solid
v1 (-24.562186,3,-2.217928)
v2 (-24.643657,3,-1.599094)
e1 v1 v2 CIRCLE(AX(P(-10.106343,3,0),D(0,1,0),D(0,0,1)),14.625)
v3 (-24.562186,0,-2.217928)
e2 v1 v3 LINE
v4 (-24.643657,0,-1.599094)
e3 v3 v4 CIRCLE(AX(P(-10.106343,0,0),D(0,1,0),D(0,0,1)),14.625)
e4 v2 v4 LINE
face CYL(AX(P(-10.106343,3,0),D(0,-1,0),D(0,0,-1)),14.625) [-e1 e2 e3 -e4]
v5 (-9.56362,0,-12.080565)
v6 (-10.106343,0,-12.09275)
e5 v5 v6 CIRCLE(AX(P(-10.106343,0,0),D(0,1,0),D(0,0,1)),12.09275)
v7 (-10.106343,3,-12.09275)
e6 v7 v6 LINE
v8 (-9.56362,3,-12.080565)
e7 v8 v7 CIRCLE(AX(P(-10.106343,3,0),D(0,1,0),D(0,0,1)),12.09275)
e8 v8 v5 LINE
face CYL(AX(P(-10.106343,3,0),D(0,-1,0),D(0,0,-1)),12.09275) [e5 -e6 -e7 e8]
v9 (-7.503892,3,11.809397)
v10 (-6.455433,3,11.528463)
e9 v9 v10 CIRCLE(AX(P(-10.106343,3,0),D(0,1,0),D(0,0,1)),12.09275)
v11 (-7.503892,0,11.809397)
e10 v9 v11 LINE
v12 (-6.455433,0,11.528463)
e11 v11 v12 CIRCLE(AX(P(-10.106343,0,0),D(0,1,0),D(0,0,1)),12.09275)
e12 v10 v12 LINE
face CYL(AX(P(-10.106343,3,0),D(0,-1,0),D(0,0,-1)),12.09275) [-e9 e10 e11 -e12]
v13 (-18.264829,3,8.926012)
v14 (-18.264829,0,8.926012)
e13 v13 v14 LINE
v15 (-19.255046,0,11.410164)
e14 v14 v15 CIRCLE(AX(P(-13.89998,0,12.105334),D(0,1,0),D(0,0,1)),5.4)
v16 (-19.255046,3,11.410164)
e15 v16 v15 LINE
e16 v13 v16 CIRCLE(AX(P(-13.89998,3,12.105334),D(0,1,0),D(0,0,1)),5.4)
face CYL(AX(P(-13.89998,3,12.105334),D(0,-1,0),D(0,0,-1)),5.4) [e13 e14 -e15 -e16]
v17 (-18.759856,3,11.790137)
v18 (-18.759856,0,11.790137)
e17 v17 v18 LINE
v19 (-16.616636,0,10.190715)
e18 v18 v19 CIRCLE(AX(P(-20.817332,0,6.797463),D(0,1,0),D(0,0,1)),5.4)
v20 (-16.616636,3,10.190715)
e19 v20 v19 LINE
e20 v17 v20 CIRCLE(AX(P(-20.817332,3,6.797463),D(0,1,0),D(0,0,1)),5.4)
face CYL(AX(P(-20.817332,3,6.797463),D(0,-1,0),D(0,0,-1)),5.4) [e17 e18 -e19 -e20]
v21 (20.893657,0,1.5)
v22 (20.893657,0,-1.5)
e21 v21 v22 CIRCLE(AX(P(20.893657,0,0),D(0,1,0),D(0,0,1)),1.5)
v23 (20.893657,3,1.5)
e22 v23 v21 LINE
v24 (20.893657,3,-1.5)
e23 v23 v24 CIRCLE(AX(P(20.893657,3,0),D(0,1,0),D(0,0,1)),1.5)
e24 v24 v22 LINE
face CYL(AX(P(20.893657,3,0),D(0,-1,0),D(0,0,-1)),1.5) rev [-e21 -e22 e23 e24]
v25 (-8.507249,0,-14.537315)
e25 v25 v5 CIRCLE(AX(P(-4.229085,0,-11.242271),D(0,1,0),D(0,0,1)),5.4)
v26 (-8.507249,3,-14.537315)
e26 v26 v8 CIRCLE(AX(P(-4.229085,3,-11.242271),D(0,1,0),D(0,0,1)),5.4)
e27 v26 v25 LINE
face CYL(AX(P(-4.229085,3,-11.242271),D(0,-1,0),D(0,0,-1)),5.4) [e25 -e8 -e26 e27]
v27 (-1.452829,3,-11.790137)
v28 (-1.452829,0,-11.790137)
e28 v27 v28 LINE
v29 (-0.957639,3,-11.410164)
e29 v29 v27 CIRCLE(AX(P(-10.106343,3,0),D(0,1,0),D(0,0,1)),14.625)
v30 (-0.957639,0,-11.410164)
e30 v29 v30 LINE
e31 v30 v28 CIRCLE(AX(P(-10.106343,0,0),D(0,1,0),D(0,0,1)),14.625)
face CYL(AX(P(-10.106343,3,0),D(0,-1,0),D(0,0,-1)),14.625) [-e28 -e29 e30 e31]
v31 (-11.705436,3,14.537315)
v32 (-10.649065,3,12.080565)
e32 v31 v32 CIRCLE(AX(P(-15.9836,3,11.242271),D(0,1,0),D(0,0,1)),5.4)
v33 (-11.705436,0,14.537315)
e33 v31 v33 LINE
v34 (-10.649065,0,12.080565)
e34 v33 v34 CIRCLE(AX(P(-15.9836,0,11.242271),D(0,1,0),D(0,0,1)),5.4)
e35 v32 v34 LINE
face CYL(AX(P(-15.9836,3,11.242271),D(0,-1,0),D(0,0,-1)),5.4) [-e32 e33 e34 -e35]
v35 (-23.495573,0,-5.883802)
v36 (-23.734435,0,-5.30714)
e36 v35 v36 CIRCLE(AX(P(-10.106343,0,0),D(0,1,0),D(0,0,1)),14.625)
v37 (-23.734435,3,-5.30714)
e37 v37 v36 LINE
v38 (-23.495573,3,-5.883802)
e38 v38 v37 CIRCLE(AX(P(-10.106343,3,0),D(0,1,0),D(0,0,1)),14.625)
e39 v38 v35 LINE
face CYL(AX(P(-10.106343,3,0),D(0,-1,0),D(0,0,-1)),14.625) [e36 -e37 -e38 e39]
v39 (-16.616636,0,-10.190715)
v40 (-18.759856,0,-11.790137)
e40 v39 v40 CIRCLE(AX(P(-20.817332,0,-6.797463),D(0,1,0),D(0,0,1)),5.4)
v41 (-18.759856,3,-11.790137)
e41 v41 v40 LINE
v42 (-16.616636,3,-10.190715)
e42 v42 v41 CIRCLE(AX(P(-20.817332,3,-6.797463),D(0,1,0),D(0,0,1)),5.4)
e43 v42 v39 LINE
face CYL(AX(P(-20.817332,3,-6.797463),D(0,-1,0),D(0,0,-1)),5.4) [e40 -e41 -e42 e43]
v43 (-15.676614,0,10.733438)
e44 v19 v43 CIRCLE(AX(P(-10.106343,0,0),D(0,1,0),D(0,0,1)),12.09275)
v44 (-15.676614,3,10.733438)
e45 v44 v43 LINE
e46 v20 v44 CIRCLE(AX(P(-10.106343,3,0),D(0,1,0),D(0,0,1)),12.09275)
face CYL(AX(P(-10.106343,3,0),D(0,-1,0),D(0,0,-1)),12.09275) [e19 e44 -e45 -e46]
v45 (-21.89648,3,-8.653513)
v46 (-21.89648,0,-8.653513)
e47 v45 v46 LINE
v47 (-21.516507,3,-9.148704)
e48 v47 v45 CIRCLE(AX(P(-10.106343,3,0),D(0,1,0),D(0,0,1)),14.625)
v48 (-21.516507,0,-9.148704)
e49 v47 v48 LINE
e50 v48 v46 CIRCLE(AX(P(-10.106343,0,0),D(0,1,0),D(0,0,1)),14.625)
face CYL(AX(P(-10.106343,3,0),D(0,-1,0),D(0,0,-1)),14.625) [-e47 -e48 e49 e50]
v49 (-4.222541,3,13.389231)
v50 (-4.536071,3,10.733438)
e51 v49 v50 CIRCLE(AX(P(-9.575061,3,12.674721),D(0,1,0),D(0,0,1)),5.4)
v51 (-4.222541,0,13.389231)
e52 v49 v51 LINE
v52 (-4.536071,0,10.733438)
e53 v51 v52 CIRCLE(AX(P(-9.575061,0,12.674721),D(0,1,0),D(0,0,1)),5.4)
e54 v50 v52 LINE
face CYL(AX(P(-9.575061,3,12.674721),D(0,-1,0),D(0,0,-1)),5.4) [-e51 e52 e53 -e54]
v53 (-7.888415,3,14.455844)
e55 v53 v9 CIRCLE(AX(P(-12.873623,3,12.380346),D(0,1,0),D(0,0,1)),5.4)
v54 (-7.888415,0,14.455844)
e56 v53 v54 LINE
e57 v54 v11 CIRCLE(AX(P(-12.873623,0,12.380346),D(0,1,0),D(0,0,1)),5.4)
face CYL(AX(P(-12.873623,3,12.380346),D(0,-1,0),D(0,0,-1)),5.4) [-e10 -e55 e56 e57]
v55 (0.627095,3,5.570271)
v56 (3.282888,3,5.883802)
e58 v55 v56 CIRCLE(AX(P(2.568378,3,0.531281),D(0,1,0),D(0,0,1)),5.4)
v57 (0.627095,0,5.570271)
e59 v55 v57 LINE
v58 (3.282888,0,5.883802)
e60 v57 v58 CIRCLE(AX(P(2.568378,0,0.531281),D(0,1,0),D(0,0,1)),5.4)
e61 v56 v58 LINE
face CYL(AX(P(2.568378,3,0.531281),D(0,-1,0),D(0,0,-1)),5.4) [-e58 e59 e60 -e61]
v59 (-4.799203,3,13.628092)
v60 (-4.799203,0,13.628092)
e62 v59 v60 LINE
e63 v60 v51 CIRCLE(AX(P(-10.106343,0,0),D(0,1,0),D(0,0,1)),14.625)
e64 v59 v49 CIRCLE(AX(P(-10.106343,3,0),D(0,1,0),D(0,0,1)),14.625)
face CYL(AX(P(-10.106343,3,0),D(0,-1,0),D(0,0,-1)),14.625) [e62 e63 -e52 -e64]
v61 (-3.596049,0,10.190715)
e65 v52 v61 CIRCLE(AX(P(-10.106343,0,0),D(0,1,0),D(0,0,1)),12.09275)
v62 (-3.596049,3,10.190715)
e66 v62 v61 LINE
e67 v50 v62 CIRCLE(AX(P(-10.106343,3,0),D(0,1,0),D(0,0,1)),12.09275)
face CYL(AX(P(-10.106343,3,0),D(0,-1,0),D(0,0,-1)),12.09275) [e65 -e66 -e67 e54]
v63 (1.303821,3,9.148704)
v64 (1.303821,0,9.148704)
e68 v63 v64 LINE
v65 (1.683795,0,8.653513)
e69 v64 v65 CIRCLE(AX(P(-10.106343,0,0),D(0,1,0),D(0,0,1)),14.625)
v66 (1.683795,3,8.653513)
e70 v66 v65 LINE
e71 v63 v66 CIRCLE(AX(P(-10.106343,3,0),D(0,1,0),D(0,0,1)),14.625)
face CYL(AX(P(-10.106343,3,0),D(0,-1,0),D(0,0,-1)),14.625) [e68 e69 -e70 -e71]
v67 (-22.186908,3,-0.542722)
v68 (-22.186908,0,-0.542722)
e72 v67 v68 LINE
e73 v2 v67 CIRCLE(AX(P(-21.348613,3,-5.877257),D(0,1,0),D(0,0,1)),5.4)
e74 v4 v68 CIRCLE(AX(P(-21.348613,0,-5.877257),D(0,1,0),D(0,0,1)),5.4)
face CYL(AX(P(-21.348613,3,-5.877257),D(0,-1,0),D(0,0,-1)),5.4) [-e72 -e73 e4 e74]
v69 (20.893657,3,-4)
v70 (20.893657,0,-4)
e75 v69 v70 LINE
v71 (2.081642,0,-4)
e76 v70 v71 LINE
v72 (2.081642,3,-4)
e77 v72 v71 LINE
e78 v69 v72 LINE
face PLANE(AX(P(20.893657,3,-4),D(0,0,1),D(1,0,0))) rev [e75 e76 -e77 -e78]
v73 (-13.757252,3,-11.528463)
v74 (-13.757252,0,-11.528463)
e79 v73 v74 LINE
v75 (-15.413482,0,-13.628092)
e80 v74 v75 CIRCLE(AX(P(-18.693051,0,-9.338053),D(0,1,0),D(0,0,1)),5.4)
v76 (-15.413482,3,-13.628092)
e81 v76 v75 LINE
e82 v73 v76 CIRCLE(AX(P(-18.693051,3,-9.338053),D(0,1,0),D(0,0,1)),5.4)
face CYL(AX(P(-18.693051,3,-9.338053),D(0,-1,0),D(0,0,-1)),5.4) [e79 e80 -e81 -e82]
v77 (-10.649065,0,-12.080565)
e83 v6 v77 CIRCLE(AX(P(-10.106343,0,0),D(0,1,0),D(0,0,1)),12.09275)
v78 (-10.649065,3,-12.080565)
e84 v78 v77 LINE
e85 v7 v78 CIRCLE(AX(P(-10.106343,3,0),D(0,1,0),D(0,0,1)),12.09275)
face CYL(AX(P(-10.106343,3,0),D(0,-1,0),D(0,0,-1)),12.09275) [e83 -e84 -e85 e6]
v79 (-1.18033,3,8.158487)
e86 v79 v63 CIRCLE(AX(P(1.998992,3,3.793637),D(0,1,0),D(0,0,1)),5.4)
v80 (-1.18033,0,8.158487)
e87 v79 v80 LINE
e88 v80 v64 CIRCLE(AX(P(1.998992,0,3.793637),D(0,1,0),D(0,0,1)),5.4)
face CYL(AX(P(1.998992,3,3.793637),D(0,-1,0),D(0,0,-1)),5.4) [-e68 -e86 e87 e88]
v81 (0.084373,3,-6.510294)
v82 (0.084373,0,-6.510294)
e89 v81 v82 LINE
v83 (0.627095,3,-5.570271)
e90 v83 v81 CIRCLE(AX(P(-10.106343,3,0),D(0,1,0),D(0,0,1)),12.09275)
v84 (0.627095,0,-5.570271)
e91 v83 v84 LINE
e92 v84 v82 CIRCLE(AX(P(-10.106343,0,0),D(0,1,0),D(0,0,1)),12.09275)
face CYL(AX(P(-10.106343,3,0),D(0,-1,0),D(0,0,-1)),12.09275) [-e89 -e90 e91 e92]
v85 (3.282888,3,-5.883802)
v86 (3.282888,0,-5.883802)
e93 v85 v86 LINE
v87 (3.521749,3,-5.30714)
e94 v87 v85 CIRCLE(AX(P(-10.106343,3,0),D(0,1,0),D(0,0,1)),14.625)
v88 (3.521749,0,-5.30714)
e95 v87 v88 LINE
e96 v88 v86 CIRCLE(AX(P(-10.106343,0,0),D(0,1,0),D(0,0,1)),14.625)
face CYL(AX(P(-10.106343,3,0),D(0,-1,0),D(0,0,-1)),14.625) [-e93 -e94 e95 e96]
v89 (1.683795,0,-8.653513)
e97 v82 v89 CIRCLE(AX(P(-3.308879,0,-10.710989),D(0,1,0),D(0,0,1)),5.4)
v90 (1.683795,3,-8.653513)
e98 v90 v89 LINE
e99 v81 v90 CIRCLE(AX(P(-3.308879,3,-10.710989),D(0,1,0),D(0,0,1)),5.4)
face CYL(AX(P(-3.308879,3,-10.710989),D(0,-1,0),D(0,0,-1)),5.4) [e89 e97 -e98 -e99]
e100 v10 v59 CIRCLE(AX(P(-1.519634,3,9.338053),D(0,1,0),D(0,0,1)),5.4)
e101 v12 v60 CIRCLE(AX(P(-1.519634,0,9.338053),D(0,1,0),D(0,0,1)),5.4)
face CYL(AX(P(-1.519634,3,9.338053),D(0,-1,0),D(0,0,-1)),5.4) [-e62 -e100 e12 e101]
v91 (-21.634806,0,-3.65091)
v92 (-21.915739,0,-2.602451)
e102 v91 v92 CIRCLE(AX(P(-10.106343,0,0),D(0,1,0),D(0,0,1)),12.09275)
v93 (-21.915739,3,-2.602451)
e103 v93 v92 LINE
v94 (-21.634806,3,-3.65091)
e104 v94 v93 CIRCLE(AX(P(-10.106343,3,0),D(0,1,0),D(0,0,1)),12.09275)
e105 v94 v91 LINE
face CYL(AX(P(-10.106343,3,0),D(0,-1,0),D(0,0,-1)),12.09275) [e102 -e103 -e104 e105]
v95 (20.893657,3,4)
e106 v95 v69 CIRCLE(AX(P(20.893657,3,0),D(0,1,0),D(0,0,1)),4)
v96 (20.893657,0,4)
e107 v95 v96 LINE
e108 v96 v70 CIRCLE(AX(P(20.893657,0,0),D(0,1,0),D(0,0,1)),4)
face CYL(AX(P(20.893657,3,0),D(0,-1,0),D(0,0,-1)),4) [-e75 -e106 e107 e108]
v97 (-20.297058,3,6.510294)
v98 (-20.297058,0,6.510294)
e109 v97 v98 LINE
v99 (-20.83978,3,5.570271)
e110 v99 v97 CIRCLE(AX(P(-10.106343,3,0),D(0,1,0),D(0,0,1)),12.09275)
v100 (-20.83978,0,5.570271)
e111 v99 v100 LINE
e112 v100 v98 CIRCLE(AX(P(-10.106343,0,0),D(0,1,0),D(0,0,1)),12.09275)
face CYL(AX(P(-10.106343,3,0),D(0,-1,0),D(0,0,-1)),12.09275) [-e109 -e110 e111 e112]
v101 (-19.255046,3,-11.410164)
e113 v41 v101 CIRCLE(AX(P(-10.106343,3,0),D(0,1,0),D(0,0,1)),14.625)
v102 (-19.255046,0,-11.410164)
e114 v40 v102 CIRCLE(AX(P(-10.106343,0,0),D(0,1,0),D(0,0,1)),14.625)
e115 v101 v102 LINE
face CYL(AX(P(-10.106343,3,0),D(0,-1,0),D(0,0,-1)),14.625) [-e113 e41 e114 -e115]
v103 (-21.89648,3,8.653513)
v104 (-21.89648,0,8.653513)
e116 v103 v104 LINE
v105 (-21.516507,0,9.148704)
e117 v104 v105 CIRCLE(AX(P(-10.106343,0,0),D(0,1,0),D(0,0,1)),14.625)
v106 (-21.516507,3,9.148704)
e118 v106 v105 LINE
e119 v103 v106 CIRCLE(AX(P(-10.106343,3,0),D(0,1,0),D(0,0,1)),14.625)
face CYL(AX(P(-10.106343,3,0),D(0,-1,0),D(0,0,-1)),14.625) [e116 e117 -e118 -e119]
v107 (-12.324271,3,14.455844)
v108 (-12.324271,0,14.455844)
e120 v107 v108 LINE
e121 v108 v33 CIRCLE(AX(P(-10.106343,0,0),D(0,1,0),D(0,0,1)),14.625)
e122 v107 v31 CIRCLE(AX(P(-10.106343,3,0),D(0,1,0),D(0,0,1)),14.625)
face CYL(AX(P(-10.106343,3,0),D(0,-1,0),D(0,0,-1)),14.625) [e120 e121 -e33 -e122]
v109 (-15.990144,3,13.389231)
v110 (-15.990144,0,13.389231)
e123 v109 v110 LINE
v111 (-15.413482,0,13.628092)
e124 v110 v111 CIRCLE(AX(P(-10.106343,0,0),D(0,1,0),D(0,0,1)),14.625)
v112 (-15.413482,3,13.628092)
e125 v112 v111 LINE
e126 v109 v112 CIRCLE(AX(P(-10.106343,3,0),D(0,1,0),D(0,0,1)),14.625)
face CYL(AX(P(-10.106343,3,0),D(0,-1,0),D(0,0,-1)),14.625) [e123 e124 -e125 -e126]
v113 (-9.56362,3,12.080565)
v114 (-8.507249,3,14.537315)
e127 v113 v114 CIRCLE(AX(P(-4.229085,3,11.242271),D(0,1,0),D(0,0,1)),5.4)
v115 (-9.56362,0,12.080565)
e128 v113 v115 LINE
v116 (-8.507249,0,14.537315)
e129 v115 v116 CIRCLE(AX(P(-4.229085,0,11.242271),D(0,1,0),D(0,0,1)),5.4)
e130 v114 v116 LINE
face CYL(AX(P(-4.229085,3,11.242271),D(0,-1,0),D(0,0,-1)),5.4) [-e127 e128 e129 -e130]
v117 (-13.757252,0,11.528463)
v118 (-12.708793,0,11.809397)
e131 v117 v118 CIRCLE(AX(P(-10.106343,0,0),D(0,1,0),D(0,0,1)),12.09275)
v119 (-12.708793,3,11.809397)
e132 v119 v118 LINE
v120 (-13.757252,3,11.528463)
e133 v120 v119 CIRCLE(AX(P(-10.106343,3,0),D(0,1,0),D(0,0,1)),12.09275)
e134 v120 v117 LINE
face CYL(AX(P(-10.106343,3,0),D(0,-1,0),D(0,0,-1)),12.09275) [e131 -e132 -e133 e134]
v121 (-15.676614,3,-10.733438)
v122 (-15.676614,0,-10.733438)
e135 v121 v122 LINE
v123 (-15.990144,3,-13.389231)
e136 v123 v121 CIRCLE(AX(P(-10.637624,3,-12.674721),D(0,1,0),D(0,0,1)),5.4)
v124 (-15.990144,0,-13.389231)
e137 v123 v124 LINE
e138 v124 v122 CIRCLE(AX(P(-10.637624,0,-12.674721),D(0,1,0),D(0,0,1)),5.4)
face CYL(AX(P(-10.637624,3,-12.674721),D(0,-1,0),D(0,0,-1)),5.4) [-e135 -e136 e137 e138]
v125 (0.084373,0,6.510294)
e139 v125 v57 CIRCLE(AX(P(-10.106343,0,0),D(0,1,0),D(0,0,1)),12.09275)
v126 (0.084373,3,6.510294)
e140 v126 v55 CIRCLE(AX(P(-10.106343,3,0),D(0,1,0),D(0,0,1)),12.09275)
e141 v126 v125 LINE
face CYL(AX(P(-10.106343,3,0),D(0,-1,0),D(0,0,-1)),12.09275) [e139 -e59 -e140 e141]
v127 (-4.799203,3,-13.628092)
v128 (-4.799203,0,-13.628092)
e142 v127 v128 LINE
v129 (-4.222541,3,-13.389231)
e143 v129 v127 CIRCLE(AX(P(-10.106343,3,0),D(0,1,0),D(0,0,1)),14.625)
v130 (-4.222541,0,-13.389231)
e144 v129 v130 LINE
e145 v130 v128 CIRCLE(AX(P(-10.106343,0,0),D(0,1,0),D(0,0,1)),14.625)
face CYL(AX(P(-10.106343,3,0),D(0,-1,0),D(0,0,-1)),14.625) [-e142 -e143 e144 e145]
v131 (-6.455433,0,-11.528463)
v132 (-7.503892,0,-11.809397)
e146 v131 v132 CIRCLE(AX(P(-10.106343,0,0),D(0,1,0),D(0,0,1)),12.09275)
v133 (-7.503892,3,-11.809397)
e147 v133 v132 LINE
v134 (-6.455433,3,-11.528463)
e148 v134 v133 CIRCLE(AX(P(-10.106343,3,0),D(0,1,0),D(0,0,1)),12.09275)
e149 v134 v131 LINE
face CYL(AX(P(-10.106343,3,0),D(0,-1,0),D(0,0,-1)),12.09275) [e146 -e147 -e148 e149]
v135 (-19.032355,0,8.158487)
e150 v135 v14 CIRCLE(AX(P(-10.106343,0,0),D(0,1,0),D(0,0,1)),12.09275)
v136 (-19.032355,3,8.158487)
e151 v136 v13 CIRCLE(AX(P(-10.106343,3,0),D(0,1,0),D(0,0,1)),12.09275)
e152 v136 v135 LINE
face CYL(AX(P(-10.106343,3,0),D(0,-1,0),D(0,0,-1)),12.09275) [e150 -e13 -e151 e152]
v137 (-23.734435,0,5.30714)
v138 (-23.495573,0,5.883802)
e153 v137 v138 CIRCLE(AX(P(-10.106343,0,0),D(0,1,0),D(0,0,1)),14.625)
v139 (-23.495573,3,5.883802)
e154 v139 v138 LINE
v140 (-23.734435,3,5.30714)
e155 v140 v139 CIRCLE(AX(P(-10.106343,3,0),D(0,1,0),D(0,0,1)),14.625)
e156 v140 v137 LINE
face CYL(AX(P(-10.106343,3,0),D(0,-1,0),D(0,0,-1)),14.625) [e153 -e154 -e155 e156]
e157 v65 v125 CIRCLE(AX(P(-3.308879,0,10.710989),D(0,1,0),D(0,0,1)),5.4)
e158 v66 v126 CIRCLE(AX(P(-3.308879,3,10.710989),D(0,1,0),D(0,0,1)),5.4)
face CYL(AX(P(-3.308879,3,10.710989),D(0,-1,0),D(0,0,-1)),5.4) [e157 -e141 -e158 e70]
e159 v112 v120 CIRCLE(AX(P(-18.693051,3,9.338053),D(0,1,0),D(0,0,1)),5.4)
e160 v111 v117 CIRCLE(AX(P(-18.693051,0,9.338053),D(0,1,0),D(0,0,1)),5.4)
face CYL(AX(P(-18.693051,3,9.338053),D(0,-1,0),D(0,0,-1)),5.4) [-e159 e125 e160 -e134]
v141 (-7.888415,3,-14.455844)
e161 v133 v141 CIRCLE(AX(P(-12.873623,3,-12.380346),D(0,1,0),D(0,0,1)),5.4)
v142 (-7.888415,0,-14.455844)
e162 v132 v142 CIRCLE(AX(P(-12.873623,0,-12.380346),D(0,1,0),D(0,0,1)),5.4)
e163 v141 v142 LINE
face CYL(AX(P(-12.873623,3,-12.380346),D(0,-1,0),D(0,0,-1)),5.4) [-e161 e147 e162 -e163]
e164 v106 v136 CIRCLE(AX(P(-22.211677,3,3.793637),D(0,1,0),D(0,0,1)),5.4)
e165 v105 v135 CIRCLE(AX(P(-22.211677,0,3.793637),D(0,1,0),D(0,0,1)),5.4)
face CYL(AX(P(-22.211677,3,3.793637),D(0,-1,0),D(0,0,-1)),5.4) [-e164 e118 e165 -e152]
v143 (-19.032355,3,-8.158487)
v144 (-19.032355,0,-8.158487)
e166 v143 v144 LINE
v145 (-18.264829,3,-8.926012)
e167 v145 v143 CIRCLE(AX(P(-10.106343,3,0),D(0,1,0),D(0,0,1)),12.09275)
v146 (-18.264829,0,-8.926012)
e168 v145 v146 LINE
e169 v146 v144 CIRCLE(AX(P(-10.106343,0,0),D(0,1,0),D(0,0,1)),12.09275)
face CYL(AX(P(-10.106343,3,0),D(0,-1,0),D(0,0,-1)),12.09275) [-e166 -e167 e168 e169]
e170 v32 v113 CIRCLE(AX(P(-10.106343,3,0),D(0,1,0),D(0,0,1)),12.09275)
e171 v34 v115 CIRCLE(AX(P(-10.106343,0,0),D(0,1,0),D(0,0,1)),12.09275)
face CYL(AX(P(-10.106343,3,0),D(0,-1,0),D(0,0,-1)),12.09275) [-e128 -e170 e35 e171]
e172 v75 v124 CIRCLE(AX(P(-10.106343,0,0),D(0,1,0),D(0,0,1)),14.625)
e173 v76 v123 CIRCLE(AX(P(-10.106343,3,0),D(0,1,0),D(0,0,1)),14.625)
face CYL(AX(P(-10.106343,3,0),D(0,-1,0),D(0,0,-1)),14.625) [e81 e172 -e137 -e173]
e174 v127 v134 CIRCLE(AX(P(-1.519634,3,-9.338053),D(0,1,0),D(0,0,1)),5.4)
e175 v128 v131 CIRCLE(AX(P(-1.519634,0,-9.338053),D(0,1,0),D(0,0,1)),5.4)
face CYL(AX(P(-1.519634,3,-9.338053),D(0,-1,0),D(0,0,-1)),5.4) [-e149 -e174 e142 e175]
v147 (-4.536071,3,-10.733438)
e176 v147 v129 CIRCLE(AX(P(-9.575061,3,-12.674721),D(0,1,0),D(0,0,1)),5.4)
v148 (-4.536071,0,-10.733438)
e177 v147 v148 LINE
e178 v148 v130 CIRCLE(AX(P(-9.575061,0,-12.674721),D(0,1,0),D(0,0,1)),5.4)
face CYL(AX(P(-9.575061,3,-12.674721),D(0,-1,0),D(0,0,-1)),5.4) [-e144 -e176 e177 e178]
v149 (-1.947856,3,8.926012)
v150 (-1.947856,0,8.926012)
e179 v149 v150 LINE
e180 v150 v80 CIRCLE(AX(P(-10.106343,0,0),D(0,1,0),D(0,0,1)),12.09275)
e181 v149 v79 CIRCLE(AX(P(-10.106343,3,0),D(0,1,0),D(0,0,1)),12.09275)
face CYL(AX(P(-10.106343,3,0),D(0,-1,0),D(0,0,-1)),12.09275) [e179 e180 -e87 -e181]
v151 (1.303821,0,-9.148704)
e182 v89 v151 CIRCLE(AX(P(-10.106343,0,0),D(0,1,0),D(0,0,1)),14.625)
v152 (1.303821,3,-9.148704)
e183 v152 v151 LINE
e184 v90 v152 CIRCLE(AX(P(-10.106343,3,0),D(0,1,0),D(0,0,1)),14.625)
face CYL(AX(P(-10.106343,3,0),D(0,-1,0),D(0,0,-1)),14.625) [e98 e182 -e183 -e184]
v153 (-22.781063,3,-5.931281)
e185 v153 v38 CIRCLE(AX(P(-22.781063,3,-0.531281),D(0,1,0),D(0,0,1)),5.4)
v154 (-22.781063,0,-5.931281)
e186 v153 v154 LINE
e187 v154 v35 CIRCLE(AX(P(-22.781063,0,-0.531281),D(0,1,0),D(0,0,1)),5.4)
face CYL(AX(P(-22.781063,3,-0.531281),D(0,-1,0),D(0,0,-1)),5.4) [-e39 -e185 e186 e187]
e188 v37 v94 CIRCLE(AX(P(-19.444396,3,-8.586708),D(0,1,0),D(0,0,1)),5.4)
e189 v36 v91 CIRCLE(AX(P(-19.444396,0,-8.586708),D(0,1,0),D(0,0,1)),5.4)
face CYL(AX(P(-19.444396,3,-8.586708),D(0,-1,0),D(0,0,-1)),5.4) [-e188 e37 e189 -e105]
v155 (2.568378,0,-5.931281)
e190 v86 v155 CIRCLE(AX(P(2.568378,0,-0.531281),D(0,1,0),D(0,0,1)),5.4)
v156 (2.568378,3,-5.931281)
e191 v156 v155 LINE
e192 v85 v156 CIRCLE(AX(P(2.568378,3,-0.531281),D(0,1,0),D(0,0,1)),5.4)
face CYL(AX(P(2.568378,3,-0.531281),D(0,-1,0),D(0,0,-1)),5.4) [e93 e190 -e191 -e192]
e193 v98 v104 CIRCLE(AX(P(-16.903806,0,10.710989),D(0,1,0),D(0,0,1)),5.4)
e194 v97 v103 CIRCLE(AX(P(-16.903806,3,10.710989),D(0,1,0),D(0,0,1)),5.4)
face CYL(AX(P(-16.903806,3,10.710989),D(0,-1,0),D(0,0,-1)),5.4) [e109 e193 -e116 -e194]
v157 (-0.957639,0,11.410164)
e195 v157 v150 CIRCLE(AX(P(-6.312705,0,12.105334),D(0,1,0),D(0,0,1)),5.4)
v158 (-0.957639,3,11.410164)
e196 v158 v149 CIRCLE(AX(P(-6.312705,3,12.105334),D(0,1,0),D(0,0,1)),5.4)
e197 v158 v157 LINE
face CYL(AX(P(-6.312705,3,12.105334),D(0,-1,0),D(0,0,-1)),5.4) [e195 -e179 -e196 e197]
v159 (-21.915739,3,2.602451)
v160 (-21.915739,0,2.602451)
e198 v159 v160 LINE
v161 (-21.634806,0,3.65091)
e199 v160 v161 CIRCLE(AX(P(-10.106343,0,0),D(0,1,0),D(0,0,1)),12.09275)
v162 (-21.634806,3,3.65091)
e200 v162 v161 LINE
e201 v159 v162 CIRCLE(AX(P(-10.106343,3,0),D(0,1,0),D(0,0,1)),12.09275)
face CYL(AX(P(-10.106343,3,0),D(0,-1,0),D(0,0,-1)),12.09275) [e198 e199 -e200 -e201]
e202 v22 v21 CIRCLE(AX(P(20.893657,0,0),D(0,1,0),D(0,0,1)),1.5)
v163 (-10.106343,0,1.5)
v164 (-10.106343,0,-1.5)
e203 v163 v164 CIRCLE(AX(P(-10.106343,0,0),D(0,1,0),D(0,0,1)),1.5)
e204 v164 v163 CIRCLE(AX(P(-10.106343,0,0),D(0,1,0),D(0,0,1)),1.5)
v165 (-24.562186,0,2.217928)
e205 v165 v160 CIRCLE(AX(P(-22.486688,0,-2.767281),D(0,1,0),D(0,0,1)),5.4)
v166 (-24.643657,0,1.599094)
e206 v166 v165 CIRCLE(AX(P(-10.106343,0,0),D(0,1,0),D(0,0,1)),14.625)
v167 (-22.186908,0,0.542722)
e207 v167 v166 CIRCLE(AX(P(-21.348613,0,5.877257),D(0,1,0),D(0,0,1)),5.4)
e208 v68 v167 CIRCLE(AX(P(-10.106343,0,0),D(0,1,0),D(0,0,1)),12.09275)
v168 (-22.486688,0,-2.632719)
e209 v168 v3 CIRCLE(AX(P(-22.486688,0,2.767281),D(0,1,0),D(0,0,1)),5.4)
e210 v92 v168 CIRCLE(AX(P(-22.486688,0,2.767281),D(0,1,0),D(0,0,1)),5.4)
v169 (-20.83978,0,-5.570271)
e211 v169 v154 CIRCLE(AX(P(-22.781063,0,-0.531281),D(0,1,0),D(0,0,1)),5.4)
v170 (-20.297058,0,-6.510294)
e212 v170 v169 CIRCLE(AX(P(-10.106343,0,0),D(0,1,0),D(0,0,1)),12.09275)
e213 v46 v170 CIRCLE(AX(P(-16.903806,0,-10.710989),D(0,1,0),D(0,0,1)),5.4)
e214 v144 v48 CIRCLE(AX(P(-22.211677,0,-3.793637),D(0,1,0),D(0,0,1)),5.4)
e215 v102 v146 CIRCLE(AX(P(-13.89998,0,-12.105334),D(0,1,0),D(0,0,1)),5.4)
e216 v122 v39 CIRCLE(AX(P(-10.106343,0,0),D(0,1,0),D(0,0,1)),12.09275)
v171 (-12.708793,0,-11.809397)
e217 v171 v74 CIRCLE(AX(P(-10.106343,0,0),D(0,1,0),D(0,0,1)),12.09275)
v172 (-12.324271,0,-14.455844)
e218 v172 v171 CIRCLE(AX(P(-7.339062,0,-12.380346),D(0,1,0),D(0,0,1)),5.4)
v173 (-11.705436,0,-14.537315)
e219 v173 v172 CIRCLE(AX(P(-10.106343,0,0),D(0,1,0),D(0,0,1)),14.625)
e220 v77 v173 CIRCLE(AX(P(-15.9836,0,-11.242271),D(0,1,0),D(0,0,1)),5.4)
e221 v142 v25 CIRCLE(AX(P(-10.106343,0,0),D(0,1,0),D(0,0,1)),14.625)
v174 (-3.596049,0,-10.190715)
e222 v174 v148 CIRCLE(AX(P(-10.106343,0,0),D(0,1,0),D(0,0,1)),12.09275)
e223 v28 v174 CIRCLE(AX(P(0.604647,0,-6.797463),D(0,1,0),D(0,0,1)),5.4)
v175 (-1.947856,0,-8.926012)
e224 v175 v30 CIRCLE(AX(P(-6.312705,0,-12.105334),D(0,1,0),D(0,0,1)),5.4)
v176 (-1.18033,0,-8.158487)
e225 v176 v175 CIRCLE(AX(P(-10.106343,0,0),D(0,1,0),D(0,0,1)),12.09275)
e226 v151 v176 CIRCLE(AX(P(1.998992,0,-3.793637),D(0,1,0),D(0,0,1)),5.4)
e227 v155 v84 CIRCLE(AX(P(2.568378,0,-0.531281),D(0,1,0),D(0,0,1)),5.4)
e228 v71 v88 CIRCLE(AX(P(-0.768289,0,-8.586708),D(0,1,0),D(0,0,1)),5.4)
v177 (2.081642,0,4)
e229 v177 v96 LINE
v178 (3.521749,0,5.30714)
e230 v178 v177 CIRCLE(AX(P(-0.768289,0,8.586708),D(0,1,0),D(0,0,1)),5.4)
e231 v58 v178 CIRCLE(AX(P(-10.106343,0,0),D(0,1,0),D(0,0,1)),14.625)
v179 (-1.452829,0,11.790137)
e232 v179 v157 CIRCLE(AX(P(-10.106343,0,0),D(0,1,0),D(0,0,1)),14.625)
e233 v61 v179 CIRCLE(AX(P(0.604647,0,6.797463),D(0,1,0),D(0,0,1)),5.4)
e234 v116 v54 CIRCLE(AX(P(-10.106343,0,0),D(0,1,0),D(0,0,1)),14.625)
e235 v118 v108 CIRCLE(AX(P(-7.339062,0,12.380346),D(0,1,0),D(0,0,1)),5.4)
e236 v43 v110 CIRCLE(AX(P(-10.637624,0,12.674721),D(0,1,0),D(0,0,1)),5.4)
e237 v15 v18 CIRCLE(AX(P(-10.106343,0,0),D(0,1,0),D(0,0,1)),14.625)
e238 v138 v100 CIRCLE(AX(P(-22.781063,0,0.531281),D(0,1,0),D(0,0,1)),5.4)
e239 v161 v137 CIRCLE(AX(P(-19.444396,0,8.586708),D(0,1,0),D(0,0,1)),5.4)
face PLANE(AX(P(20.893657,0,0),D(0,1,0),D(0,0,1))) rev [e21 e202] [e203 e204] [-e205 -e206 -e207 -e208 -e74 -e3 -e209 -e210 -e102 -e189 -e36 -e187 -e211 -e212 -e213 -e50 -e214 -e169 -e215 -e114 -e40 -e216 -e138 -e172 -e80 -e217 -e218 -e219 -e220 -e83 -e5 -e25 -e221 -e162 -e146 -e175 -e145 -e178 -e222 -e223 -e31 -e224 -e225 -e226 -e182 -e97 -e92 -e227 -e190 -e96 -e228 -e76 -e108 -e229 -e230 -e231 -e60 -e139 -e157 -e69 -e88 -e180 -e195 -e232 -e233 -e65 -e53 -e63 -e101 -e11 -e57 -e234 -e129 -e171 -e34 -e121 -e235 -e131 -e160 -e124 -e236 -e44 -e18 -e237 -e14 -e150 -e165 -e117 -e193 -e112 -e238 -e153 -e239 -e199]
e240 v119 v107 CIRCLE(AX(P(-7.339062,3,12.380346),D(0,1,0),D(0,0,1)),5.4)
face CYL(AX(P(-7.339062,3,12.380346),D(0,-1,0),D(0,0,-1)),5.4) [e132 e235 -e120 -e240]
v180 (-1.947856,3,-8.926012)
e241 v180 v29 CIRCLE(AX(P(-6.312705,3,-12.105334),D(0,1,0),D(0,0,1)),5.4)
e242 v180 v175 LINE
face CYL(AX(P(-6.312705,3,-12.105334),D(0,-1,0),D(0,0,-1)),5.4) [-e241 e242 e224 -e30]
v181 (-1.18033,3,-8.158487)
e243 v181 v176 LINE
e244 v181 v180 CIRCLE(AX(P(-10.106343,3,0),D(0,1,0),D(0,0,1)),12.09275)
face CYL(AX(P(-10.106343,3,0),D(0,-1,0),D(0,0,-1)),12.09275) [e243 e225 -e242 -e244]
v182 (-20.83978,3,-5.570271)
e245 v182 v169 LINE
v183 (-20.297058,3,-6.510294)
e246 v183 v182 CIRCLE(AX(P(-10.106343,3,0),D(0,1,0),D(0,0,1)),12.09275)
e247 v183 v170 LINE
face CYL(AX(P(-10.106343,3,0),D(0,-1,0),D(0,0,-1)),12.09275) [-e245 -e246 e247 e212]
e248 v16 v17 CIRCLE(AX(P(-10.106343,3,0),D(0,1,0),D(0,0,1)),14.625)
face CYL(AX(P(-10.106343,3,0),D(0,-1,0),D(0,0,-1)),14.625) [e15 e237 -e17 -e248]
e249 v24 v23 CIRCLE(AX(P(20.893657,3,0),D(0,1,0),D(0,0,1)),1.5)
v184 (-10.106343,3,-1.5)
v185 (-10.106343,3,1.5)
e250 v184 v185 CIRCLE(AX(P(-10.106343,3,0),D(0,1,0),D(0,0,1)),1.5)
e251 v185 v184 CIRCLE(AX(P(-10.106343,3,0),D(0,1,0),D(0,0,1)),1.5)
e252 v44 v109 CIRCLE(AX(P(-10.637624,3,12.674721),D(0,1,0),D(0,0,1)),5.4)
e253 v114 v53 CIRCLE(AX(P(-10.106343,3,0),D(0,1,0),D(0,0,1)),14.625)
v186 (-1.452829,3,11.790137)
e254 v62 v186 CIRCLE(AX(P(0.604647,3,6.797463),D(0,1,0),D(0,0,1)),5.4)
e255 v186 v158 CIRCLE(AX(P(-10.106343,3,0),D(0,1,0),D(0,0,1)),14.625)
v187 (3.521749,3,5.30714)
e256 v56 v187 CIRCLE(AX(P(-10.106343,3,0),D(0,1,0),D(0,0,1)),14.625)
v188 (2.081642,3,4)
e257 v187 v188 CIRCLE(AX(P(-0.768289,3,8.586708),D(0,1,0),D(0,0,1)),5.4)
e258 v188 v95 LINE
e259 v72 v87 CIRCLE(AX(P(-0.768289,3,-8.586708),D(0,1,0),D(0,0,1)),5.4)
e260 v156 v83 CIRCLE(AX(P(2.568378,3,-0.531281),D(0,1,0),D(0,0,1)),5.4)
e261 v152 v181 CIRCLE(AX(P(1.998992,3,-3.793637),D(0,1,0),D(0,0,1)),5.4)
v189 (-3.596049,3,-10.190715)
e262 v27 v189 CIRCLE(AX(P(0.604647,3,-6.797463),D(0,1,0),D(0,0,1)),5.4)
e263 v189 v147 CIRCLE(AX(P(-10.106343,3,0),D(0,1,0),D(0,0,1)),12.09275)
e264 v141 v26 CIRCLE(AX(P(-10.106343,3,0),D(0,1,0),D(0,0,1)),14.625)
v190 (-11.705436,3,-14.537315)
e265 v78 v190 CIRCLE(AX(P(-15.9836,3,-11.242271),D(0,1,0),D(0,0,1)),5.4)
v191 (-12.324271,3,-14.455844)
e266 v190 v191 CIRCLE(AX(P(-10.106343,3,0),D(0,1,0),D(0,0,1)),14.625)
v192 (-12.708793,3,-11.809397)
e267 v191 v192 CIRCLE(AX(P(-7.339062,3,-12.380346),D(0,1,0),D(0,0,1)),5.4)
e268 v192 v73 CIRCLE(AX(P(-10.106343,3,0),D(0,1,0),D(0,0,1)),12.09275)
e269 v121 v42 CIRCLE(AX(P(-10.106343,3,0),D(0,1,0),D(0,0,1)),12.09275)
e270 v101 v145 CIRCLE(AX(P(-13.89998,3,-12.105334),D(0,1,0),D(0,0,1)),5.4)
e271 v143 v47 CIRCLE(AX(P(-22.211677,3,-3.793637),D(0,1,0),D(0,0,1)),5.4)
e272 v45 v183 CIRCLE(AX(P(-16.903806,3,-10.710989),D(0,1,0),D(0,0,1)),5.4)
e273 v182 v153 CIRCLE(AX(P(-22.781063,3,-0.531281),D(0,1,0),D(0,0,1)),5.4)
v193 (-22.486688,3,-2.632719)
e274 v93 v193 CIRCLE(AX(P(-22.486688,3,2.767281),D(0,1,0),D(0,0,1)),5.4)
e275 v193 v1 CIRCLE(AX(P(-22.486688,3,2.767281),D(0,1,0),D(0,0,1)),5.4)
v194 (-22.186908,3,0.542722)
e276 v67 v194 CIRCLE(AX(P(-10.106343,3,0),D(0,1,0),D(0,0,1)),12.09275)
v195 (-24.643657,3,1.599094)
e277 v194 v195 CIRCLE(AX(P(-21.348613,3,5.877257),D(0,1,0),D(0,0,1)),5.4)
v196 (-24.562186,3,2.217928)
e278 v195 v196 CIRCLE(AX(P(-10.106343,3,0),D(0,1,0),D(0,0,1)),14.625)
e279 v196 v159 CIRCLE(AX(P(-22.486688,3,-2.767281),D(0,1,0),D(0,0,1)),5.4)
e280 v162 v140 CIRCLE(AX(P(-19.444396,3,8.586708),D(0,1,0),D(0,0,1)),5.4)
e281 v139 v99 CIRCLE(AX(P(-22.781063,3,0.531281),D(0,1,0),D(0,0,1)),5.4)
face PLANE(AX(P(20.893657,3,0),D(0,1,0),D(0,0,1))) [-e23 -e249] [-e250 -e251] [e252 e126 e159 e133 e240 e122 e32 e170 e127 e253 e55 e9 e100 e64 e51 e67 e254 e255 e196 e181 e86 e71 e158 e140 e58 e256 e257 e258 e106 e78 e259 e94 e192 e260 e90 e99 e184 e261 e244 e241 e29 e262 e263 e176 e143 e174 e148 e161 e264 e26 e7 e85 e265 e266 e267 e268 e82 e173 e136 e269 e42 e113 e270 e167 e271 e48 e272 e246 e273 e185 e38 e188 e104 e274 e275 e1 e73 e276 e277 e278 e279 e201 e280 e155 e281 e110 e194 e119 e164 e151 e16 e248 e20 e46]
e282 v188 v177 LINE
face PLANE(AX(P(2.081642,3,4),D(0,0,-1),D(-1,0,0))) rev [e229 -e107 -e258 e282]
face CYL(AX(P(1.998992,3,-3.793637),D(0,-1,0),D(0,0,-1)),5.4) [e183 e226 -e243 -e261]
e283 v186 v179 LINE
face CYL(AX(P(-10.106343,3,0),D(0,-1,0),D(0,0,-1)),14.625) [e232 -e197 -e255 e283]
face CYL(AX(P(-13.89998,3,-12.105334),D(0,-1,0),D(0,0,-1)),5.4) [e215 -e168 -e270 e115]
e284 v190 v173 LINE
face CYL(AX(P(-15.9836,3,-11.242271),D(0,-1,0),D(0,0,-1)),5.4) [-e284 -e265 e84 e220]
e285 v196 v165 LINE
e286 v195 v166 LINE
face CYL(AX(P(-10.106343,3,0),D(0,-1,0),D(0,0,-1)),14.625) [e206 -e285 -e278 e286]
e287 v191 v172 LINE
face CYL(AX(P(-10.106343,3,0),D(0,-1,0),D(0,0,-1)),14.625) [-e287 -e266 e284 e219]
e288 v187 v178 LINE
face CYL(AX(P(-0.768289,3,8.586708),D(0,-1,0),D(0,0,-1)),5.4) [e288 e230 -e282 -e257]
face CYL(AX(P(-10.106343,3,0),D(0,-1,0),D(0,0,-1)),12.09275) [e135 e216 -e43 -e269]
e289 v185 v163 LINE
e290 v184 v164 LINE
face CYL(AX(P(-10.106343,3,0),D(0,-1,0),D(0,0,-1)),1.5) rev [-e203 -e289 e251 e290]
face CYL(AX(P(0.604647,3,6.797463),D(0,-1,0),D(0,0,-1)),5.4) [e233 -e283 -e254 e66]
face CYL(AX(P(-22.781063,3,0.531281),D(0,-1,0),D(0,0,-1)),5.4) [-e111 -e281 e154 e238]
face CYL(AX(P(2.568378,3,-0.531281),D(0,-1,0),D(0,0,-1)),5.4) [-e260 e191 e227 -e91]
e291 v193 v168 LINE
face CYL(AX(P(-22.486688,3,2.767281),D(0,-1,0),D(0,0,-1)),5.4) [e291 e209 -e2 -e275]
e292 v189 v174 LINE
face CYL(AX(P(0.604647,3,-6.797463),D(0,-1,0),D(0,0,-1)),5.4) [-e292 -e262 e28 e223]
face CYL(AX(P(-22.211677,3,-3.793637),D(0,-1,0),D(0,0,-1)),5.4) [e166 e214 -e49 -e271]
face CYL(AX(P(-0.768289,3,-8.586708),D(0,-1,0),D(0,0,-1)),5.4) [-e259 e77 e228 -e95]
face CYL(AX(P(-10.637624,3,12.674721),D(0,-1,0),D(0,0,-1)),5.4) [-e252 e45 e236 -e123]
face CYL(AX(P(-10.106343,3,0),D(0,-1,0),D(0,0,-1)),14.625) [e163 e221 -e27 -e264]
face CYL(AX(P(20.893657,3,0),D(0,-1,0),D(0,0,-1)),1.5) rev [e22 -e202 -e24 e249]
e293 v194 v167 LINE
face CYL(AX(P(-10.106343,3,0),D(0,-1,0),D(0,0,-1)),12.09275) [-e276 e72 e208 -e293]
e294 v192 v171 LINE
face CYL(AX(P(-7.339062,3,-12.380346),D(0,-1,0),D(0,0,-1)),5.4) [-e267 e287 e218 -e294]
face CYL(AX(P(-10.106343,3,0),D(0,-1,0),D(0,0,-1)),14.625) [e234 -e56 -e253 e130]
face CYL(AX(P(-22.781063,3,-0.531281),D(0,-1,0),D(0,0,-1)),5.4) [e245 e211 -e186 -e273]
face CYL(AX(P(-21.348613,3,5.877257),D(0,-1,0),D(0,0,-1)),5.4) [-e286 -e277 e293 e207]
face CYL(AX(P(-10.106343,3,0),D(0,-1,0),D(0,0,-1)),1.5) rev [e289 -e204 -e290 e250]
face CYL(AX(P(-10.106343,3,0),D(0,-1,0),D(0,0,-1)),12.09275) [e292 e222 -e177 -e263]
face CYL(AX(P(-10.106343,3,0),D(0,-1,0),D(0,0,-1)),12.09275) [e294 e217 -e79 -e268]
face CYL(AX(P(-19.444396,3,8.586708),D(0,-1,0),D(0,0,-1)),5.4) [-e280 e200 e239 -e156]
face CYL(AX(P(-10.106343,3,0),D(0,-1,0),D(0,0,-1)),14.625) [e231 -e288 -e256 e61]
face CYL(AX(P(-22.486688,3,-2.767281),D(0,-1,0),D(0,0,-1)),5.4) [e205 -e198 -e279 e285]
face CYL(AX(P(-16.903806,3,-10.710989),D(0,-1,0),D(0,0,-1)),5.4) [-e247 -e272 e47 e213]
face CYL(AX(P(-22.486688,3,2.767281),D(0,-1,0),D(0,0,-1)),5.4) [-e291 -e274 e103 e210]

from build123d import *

# Parameters (mm, degrees)
SKETCH1_R           = 1.5
BOSS_EXTRUDE1_DEPTH = 3


with BuildPart() as part:
    # Sketch1 → Boss-Extrude1 (new body)
    with BuildSketch(Plane(origin=(0, 0, 0), x_dir=(1, 0, 0), z_dir=(0, 1, 0))):
        with BuildLine():
            Line((20.893657446, 4), (2.081641936, 4))
            ThreePointArc((2.081641936, 4), (2.861028333, 4.588201733), (3.521749436, 5.30713988))
            ThreePointArc((3.521749436, 5.30713988), (3.405395609, 5.596745198), (3.282888305, 5.883801663))
            ThreePointArc((3.282888305, 5.883801663), (1.93527598, 5.894040025), (0.627094961, 5.57027124))
            ThreePointArc((0.627094961, 5.57027124), (0.366286148, 6.046375), (0.084372603, 6.510293938))
            ThreePointArc((0.084372603, 6.510293938), (1.018855105, 7.48132754), (1.683794586, 8.65351323))
            ThreePointArc((1.683794586, 8.65351323), (1.496450048, 8.903135899), (1.303821399, 9.148703928))
            ThreePointArc((1.303821399, 9.148703928), (-0.000522033, 8.809805691), (-1.180330337, 8.158486898))
            ThreePointArc((-1.180330337, 8.158486898), (-1.555477026, 8.550865528), (-1.947855656, 8.926012217))
            ThreePointArc((-1.947855656, 8.926012217), (-1.296536862, 10.105820521), (-0.957638625, 11.410163953))
            ThreePointArc((-0.957638625, 11.410163953), (-1.203206655, 11.602792602), (-1.452829324, 11.79013714))
            ThreePointArc((-1.452829324, 11.79013714), (-2.625015014, 11.125197659), (-3.596048616, 10.190715157))
            ThreePointArc((-3.596048616, 10.190715157), (-4.059967554, 10.472628702), (-4.536071314, 10.733437515))
            ThreePointArc((-4.536071314, 10.733437515), (-4.212302529, 12.041618533), (-4.222540891, 13.389230859))
            ThreePointArc((-4.222540891, 13.389230859), (-4.509597355, 13.511738163), (-4.799202674, 13.62809199))
            ThreePointArc((-4.799202674, 13.62809199), (-5.759348103, 12.682425791), (-6.455432668, 11.528463019))
            ThreePointArc((-6.455432668, 11.528463019), (-6.976508546, 11.680699536), (-7.503891752, 11.809396783))
            ThreePointArc((-7.503891752, 11.809396783), (-7.529737283, 13.156800143), (-7.888414517, 14.455843809))
            ThreePointArc((-7.888414517, 14.455843809), (-8.197396993, 14.499881098), (-8.507248835, 14.537314892))
            ThreePointArc((-8.507248835, 14.537314892), (-9.18992168, 13.375367565), (-9.563620196, 12.080565177))
            ThreePointArc((-9.563620196, 12.080565177), (-10.106342554, 12.09275), (-10.649064912, 12.080565177))
            ThreePointArc((-10.649064912, 12.080565177), (-11.022763428, 13.375367565), (-11.705436272, 14.537314892))
            ThreePointArc((-11.705436272, 14.537314892), (-12.015288115, 14.499881098), (-12.324270591, 14.455843809))
            ThreePointArc((-12.324270591, 14.455843809), (-12.682947825, 13.156800143), (-12.708793355, 11.809396783))
            ThreePointArc((-12.708793355, 11.809396783), (-13.236176561, 11.680699536), (-13.757252439, 11.528463019))
            ThreePointArc((-13.757252439, 11.528463019), (-14.453337005, 12.682425791), (-15.413482434, 13.62809199))
            ThreePointArc((-15.413482434, 13.62809199), (-15.703087752, 13.511738163), (-15.990144217, 13.389230859))
            ThreePointArc((-15.990144217, 13.389230859), (-16.000382579, 12.041618533), (-15.676613793, 10.733437515))
            ThreePointArc((-15.676613793, 10.733437515), (-16.152717554, 10.472628702), (-16.616636492, 10.190715157))
            ThreePointArc((-16.616636492, 10.190715157), (-17.587670094, 11.125197659), (-18.759855783, 11.79013714))
            ThreePointArc((-18.759855783, 11.79013714), (-19.009478453, 11.602792602), (-19.255046482, 11.410163953))
            ThreePointArc((-19.255046482, 11.410163953), (-18.916148245, 10.105820521), (-18.264829452, 8.926012217))
            ThreePointArc((-18.264829452, 8.926012217), (-18.657208082, 8.550865528), (-19.032354771, 8.158486898))
            ThreePointArc((-19.032354771, 8.158486898), (-20.212163074, 8.809805691), (-21.516506507, 9.148703928))
            ThreePointArc((-21.516506507, 9.148703928), (-21.709135156, 8.903135899), (-21.896479694, 8.65351323))
            ThreePointArc((-21.896479694, 8.65351323), (-21.231540213, 7.48132754), (-20.297057711, 6.510293938))
            ThreePointArc((-20.297057711, 6.510293938), (-20.578971255, 6.046375), (-20.839780068, 5.57027124))
            ThreePointArc((-20.839780068, 5.57027124), (-22.147961087, 5.894040025), (-23.495573413, 5.883801663))
            ThreePointArc((-23.495573413, 5.883801663), (-23.618080717, 5.596745198), (-23.734434544, 5.30713988))
            ThreePointArc((-23.734434544, 5.30713988), (-22.788768345, 4.346994451), (-21.634805572, 3.650909885))
            ThreePointArc((-21.634805572, 3.650909885), (-21.78704209, 3.129834008), (-21.915739337, 2.602450802))
            ThreePointArc((-21.915739337, 2.602450802), (-23.263142697, 2.576605271), (-24.562186363, 2.217928037))
            ThreePointArc((-24.562186363, 2.217928037), (-24.606223651, 1.908945561), (-24.643657446, 1.599093719))
            ThreePointArc((-24.643657446, 1.599093719), (-23.481710119, 0.916420874), (-22.186907731, 0.542722358))
            ThreePointArc((-22.186907731, 0.542722358), (-22.199092554, 0), (-22.186907731, -0.542722358))
            ThreePointArc((-22.186907731, -0.542722358), (-23.481710119, -0.916420874), (-24.643657446, -1.599093719))
            ThreePointArc((-24.643657446, -1.599093719), (-24.606223651, -1.908945561), (-24.562186363, -2.217928037))
            ThreePointArc((-24.562186363, -2.217928037), (-23.263142697, -2.576605271), (-21.915739337, -2.602450802))
            ThreePointArc((-21.915739337, -2.602450802), (-21.78704209, -3.129834008), (-21.634805572, -3.650909885))
            ThreePointArc((-21.634805572, -3.650909885), (-22.788768345, -4.346994451), (-23.734434544, -5.30713988))
            ThreePointArc((-23.734434544, -5.30713988), (-23.618080717, -5.596745198), (-23.495573413, -5.883801663))
            ThreePointArc((-23.495573413, -5.883801663), (-22.147961087, -5.894040025), (-20.839780068, -5.57027124))
            ThreePointArc((-20.839780068, -5.57027124), (-20.578971255, -6.046375), (-20.297057711, -6.510293938))
            ThreePointArc((-20.297057711, -6.510293938), (-21.231540213, -7.48132754), (-21.896479694, -8.65351323))
            ThreePointArc((-21.896479694, -8.65351323), (-21.709135156, -8.903135899), (-21.516506507, -9.148703928))
            ThreePointArc((-21.516506507, -9.148703928), (-20.212163074, -8.809805691), (-19.032354771, -8.158486898))
            ThreePointArc((-19.032354771, -8.158486898), (-18.657208082, -8.550865528), (-18.264829452, -8.926012217))
            ThreePointArc((-18.264829452, -8.926012217), (-18.916148245, -10.105820521), (-19.255046482, -11.410163953))
            ThreePointArc((-19.255046482, -11.410163953), (-19.009478453, -11.602792602), (-18.759855783, -11.79013714))
            ThreePointArc((-18.759855783, -11.79013714), (-17.587670094, -11.125197659), (-16.616636492, -10.190715157))
            ThreePointArc((-16.616636492, -10.190715157), (-16.152717554, -10.472628702), (-15.676613793, -10.733437515))
            ThreePointArc((-15.676613793, -10.733437515), (-16.000382579, -12.041618533), (-15.990144217, -13.389230859))
            ThreePointArc((-15.990144217, -13.389230859), (-15.703087752, -13.511738163), (-15.413482434, -13.62809199))
            ThreePointArc((-15.413482434, -13.62809199), (-14.453337005, -12.682425791), (-13.757252439, -11.528463019))
            ThreePointArc((-13.757252439, -11.528463019), (-13.236176561, -11.680699536), (-12.708793355, -11.809396783))
            ThreePointArc((-12.708793355, -11.809396783), (-12.682947825, -13.156800143), (-12.324270591, -14.455843809))
            ThreePointArc((-12.324270591, -14.455843809), (-12.015288115, -14.499881098), (-11.705436272, -14.537314892))
            ThreePointArc((-11.705436272, -14.537314892), (-11.022763428, -13.375367565), (-10.649064912, -12.080565177))
            ThreePointArc((-10.649064912, -12.080565177), (-10.106342554, -12.09275), (-9.563620196, -12.080565177))
            ThreePointArc((-9.563620196, -12.080565177), (-9.18992168, -13.375367565), (-8.507248835, -14.537314892))
            ThreePointArc((-8.507248835, -14.537314892), (-8.197396993, -14.499881098), (-7.888414517, -14.455843809))
            ThreePointArc((-7.888414517, -14.455843809), (-7.529737283, -13.156800143), (-7.503891752, -11.809396783))
            ThreePointArc((-7.503891752, -11.809396783), (-6.976508546, -11.680699536), (-6.455432668, -11.528463019))
            ThreePointArc((-6.455432668, -11.528463019), (-5.759348103, -12.682425791), (-4.799202674, -13.62809199))
            ThreePointArc((-4.799202674, -13.62809199), (-4.509597355, -13.511738163), (-4.222540891, -13.389230859))
            ThreePointArc((-4.222540891, -13.389230859), (-4.212302529, -12.041618533), (-4.536071314, -10.733437515))
            ThreePointArc((-4.536071314, -10.733437515), (-4.059967554, -10.472628702), (-3.596048616, -10.190715157))
            ThreePointArc((-3.596048616, -10.190715157), (-2.625015014, -11.125197659), (-1.452829324, -11.79013714))
            ThreePointArc((-1.452829324, -11.79013714), (-1.203206655, -11.602792602), (-0.957638625, -11.410163953))
            ThreePointArc((-0.957638625, -11.410163953), (-1.296536862, -10.105820521), (-1.947855656, -8.926012217))
            ThreePointArc((-1.947855656, -8.926012217), (-1.555477026, -8.550865528), (-1.180330337, -8.158486898))
            ThreePointArc((-1.180330337, -8.158486898), (-0.000522033, -8.809805691), (1.303821399, -9.148703928))
            ThreePointArc((1.303821399, -9.148703928), (1.496450048, -8.903135899), (1.683794586, -8.65351323))
            ThreePointArc((1.683794586, -8.65351323), (1.018855105, -7.48132754), (0.084372603, -6.510293938))
            ThreePointArc((0.084372603, -6.510293938), (0.366286148, -6.046375), (0.627094961, -5.57027124))
            ThreePointArc((0.627094961, -5.57027124), (1.93527598, -5.894040025), (3.282888305, -5.883801663))
            ThreePointArc((3.282888305, -5.883801663), (3.405395609, -5.596745198), (3.521749436, -5.30713988))
            ThreePointArc((3.521749436, -5.30713988), (2.861028333, -4.588201733), (2.081641936, -4))
            Line((2.081641936, -4), (20.893657446, -4))
            ThreePointArc((20.893657446, -4), (24.893657446, 0), (20.893657446, 4))
        make_face()
        with Locations(Location((-10.106342554, 0, 0), (0, 0, 270))):
            Circle(SKETCH1_R, mode=Mode.SUBTRACT)
        with Locations(Location((20.893657446, 0, 0), (0, 0, 270))):
            Circle(SKETCH1_R, mode=Mode.SUBTRACT)
    extrude(amount=BOSS_EXTRUDE1_DEPTH)


solid = part.part
